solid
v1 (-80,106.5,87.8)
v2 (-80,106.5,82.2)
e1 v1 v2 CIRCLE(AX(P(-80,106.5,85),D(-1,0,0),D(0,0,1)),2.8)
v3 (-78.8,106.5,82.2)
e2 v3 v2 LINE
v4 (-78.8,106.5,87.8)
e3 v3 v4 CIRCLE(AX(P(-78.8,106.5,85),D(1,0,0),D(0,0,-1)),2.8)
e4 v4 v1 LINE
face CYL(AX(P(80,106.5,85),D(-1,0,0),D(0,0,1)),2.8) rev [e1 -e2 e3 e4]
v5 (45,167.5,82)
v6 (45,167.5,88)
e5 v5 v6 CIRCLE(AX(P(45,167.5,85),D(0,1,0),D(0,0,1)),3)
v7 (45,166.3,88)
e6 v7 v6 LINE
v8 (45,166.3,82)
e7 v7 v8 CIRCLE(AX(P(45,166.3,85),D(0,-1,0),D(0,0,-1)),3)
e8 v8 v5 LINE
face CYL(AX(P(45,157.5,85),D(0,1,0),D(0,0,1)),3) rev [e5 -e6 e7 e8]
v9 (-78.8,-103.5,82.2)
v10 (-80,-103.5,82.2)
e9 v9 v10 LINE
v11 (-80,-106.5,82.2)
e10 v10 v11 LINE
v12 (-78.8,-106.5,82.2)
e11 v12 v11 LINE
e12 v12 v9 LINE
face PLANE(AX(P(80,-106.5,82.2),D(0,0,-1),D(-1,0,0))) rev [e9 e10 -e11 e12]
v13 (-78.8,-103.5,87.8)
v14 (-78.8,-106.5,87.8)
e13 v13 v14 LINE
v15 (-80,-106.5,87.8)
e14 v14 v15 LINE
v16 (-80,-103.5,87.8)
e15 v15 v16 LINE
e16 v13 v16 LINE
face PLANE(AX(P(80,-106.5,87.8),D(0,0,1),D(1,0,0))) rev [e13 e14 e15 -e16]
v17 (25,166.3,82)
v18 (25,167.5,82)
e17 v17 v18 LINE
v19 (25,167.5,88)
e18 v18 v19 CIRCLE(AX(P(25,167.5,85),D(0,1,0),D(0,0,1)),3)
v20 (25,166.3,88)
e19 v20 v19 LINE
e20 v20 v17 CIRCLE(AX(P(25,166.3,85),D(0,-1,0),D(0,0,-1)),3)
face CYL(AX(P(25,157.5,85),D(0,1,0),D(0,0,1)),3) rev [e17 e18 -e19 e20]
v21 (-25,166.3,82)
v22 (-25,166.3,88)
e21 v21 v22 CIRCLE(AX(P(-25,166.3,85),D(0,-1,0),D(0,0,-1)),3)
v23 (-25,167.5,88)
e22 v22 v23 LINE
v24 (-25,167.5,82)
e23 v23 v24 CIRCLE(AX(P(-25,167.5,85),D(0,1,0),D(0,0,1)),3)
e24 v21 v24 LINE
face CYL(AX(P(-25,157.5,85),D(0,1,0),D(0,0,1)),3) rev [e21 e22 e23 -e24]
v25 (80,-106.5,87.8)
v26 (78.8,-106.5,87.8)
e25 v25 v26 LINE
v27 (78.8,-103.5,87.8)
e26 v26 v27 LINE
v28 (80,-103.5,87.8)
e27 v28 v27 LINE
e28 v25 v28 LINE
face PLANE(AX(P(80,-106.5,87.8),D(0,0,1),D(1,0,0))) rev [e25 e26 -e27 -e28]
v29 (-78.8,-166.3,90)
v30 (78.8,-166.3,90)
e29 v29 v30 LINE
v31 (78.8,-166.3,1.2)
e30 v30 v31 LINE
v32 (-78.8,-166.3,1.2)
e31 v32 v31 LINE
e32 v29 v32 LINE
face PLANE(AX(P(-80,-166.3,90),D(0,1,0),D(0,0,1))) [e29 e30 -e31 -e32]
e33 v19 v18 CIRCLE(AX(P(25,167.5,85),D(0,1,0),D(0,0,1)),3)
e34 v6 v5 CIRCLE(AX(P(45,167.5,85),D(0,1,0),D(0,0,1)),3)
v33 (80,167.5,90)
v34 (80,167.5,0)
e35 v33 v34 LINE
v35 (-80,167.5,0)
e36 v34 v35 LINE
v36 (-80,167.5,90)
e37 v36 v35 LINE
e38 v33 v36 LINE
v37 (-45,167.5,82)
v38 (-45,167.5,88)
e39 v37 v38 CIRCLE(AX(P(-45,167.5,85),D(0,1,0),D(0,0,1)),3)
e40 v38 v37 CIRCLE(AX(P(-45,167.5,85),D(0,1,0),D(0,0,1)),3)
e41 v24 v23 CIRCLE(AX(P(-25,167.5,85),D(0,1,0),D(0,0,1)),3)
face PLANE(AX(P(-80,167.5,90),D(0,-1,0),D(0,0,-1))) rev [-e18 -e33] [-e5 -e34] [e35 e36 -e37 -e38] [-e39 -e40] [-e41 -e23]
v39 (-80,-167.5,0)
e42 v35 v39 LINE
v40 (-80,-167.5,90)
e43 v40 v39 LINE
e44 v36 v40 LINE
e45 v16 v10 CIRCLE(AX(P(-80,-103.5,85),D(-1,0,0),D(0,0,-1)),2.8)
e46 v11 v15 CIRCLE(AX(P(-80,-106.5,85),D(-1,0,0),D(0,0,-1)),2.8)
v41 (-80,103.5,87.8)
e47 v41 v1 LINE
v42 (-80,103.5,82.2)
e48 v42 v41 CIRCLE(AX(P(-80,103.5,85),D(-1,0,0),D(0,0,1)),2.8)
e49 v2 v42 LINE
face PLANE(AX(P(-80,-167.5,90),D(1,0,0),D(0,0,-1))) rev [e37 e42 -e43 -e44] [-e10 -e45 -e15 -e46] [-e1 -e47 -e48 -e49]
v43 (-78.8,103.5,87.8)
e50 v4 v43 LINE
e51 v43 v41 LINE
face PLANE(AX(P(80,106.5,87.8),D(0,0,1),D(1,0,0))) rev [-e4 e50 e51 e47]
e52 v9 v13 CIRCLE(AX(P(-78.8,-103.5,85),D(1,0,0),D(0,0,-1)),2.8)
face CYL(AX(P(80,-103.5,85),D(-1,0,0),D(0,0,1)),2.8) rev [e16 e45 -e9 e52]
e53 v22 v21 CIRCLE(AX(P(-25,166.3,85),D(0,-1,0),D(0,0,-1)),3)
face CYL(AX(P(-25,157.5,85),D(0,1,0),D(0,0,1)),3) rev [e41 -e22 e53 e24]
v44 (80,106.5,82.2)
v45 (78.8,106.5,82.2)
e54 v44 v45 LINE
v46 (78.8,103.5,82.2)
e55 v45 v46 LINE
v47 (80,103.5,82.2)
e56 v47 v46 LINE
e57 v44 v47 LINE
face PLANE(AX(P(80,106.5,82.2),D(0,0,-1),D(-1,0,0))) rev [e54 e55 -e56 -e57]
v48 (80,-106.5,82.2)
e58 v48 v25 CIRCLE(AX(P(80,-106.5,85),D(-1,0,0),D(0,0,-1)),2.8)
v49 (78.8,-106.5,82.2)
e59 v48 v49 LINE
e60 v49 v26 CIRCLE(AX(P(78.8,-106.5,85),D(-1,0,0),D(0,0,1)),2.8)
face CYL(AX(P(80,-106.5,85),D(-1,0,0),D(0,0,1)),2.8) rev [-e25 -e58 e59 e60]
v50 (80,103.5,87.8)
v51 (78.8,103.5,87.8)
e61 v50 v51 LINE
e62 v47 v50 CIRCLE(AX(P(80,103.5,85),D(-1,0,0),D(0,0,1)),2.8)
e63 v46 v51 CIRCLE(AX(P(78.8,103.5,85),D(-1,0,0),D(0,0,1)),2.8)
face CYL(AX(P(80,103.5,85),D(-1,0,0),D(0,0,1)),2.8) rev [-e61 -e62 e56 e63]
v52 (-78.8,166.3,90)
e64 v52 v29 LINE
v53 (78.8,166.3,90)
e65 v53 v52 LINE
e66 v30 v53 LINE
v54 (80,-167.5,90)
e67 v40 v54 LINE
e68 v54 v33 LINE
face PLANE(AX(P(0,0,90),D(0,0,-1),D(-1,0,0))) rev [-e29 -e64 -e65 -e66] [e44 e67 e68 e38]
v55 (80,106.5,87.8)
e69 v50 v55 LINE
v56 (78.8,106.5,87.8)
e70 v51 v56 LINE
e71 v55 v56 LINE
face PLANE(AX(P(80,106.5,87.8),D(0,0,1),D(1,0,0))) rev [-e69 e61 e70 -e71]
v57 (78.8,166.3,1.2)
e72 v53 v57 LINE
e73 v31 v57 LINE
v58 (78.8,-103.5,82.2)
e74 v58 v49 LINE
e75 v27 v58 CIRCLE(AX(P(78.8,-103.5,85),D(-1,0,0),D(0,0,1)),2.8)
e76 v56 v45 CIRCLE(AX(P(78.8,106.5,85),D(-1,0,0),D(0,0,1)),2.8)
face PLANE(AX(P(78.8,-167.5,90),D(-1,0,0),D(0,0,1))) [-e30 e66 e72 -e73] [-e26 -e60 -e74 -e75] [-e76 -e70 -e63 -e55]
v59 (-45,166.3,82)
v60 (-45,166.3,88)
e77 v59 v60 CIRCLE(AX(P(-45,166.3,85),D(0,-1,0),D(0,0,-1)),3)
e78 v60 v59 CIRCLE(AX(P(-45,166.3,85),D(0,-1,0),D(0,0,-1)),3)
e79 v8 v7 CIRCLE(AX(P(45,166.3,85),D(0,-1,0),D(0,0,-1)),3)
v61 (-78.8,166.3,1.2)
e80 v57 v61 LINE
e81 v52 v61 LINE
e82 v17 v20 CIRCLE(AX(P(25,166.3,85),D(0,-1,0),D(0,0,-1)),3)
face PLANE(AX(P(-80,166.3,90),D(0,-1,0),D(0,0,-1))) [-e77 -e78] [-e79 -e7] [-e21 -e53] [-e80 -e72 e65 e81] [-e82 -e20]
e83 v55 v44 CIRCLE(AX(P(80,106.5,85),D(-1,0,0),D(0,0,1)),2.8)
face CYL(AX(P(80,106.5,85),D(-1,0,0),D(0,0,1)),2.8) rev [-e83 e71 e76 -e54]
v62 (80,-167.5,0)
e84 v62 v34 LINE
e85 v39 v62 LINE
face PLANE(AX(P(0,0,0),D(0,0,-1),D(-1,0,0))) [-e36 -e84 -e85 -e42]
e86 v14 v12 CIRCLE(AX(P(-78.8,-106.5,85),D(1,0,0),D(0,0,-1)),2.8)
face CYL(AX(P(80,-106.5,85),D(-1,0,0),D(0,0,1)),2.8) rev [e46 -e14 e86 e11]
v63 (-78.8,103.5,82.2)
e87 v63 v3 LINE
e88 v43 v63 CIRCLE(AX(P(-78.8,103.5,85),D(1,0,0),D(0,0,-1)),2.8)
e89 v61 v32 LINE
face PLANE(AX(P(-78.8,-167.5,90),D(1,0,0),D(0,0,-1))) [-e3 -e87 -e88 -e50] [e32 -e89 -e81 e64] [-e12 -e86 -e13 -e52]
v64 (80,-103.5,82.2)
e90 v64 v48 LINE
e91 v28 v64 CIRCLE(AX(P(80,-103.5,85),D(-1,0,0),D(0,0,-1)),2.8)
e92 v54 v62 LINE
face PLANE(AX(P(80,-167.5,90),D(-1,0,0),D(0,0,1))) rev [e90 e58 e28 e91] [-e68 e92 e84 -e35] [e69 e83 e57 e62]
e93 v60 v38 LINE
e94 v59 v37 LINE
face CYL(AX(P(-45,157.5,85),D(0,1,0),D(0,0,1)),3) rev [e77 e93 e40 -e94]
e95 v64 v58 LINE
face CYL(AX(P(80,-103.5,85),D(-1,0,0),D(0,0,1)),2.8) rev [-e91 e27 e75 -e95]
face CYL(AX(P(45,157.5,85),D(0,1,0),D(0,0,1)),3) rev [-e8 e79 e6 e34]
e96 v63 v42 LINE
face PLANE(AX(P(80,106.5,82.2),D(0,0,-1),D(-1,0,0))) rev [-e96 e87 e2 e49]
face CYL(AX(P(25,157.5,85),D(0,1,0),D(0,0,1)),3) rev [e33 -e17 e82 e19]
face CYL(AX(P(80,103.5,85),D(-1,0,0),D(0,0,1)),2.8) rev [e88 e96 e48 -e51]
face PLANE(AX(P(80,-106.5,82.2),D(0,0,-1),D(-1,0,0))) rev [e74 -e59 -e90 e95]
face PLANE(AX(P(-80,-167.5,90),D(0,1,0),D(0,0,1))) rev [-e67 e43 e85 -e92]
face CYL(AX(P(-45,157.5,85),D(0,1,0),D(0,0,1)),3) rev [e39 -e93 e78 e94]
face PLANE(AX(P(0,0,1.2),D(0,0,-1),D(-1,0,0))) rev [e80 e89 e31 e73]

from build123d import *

# Parameters (mm, degrees)
SKETCH1_W           = 160
SKETCH1_H           = 335
BOSS_EXTRUDE1_DEPTH = 90
SHELL1_T            = -1.2
SKETCH2_R           = 3
CUT_EXTRUDE1_DEPTH  = 10
CUT_EXTRUDE2_DEPTH  = 249.508048159


with BuildPart() as part:
    # Sketch1 → Boss-Extrude1 (new body)
    with BuildSketch(Plane.XY):
        Rectangle(SKETCH1_W, SKETCH1_H)
    extrude(amount=BOSS_EXTRUDE1_DEPTH)

    # Shell1
    shell1_openings = [part.faces().sort_by_distance(p)[0] for p in [
        (0, 0, 90),
    ]]
    offset(amount=SHELL1_T, openings=shell1_openings, kind=Kind.INTERSECTION)

    # Sketch2 → Cut-Extrude1 (cut)
    with BuildSketch(Plane(origin=(0, 167.5, 0), x_dir=(1, 0, 0), z_dir=(0, 1, 0))):
        with Locations(Location((-45, -85, 0), (0, 0, 270))):
            Circle(SKETCH2_R)
        with Locations(Location((-25, -85, 0), (0, 0, 270))):
            Circle(SKETCH2_R)
        with Locations(Location((25, -85, 0), (0, 0, 270))):
            Circle(SKETCH2_R)
        with Locations(Location((45, -85, 0), (0, 0, 270))):
            Circle(SKETCH2_R)
    extrude(amount=-CUT_EXTRUDE1_DEPTH, mode=Mode.SUBTRACT)

    # Sketch3 → Cut-Extrude2 (cut, through all)
    with BuildSketch(Plane.ZY.offset(80)):
        with BuildLine():
            Line((87.8, 106.5), (87.8, 103.5))
            ThreePointArc((87.8, 103.5), (85, 100.7), (82.2, 103.5))
            Line((82.2, 103.5), (82.2, 106.5))
            ThreePointArc((82.2, 106.5), (85, 109.3), (87.8, 106.5))
        make_face()
        with BuildLine():
            Line((87.8, -106.5), (87.8, -103.5))
            ThreePointArc((87.8, -103.5), (85, -100.7), (82.2, -103.5))
            Line((82.2, -103.5), (82.2, -106.5))
            ThreePointArc((82.2, -106.5), (85, -109.3), (87.8, -106.5))
        make_face()
    extrude(amount=-CUT_EXTRUDE2_DEPTH, mode=Mode.SUBTRACT)


solid = part.part
